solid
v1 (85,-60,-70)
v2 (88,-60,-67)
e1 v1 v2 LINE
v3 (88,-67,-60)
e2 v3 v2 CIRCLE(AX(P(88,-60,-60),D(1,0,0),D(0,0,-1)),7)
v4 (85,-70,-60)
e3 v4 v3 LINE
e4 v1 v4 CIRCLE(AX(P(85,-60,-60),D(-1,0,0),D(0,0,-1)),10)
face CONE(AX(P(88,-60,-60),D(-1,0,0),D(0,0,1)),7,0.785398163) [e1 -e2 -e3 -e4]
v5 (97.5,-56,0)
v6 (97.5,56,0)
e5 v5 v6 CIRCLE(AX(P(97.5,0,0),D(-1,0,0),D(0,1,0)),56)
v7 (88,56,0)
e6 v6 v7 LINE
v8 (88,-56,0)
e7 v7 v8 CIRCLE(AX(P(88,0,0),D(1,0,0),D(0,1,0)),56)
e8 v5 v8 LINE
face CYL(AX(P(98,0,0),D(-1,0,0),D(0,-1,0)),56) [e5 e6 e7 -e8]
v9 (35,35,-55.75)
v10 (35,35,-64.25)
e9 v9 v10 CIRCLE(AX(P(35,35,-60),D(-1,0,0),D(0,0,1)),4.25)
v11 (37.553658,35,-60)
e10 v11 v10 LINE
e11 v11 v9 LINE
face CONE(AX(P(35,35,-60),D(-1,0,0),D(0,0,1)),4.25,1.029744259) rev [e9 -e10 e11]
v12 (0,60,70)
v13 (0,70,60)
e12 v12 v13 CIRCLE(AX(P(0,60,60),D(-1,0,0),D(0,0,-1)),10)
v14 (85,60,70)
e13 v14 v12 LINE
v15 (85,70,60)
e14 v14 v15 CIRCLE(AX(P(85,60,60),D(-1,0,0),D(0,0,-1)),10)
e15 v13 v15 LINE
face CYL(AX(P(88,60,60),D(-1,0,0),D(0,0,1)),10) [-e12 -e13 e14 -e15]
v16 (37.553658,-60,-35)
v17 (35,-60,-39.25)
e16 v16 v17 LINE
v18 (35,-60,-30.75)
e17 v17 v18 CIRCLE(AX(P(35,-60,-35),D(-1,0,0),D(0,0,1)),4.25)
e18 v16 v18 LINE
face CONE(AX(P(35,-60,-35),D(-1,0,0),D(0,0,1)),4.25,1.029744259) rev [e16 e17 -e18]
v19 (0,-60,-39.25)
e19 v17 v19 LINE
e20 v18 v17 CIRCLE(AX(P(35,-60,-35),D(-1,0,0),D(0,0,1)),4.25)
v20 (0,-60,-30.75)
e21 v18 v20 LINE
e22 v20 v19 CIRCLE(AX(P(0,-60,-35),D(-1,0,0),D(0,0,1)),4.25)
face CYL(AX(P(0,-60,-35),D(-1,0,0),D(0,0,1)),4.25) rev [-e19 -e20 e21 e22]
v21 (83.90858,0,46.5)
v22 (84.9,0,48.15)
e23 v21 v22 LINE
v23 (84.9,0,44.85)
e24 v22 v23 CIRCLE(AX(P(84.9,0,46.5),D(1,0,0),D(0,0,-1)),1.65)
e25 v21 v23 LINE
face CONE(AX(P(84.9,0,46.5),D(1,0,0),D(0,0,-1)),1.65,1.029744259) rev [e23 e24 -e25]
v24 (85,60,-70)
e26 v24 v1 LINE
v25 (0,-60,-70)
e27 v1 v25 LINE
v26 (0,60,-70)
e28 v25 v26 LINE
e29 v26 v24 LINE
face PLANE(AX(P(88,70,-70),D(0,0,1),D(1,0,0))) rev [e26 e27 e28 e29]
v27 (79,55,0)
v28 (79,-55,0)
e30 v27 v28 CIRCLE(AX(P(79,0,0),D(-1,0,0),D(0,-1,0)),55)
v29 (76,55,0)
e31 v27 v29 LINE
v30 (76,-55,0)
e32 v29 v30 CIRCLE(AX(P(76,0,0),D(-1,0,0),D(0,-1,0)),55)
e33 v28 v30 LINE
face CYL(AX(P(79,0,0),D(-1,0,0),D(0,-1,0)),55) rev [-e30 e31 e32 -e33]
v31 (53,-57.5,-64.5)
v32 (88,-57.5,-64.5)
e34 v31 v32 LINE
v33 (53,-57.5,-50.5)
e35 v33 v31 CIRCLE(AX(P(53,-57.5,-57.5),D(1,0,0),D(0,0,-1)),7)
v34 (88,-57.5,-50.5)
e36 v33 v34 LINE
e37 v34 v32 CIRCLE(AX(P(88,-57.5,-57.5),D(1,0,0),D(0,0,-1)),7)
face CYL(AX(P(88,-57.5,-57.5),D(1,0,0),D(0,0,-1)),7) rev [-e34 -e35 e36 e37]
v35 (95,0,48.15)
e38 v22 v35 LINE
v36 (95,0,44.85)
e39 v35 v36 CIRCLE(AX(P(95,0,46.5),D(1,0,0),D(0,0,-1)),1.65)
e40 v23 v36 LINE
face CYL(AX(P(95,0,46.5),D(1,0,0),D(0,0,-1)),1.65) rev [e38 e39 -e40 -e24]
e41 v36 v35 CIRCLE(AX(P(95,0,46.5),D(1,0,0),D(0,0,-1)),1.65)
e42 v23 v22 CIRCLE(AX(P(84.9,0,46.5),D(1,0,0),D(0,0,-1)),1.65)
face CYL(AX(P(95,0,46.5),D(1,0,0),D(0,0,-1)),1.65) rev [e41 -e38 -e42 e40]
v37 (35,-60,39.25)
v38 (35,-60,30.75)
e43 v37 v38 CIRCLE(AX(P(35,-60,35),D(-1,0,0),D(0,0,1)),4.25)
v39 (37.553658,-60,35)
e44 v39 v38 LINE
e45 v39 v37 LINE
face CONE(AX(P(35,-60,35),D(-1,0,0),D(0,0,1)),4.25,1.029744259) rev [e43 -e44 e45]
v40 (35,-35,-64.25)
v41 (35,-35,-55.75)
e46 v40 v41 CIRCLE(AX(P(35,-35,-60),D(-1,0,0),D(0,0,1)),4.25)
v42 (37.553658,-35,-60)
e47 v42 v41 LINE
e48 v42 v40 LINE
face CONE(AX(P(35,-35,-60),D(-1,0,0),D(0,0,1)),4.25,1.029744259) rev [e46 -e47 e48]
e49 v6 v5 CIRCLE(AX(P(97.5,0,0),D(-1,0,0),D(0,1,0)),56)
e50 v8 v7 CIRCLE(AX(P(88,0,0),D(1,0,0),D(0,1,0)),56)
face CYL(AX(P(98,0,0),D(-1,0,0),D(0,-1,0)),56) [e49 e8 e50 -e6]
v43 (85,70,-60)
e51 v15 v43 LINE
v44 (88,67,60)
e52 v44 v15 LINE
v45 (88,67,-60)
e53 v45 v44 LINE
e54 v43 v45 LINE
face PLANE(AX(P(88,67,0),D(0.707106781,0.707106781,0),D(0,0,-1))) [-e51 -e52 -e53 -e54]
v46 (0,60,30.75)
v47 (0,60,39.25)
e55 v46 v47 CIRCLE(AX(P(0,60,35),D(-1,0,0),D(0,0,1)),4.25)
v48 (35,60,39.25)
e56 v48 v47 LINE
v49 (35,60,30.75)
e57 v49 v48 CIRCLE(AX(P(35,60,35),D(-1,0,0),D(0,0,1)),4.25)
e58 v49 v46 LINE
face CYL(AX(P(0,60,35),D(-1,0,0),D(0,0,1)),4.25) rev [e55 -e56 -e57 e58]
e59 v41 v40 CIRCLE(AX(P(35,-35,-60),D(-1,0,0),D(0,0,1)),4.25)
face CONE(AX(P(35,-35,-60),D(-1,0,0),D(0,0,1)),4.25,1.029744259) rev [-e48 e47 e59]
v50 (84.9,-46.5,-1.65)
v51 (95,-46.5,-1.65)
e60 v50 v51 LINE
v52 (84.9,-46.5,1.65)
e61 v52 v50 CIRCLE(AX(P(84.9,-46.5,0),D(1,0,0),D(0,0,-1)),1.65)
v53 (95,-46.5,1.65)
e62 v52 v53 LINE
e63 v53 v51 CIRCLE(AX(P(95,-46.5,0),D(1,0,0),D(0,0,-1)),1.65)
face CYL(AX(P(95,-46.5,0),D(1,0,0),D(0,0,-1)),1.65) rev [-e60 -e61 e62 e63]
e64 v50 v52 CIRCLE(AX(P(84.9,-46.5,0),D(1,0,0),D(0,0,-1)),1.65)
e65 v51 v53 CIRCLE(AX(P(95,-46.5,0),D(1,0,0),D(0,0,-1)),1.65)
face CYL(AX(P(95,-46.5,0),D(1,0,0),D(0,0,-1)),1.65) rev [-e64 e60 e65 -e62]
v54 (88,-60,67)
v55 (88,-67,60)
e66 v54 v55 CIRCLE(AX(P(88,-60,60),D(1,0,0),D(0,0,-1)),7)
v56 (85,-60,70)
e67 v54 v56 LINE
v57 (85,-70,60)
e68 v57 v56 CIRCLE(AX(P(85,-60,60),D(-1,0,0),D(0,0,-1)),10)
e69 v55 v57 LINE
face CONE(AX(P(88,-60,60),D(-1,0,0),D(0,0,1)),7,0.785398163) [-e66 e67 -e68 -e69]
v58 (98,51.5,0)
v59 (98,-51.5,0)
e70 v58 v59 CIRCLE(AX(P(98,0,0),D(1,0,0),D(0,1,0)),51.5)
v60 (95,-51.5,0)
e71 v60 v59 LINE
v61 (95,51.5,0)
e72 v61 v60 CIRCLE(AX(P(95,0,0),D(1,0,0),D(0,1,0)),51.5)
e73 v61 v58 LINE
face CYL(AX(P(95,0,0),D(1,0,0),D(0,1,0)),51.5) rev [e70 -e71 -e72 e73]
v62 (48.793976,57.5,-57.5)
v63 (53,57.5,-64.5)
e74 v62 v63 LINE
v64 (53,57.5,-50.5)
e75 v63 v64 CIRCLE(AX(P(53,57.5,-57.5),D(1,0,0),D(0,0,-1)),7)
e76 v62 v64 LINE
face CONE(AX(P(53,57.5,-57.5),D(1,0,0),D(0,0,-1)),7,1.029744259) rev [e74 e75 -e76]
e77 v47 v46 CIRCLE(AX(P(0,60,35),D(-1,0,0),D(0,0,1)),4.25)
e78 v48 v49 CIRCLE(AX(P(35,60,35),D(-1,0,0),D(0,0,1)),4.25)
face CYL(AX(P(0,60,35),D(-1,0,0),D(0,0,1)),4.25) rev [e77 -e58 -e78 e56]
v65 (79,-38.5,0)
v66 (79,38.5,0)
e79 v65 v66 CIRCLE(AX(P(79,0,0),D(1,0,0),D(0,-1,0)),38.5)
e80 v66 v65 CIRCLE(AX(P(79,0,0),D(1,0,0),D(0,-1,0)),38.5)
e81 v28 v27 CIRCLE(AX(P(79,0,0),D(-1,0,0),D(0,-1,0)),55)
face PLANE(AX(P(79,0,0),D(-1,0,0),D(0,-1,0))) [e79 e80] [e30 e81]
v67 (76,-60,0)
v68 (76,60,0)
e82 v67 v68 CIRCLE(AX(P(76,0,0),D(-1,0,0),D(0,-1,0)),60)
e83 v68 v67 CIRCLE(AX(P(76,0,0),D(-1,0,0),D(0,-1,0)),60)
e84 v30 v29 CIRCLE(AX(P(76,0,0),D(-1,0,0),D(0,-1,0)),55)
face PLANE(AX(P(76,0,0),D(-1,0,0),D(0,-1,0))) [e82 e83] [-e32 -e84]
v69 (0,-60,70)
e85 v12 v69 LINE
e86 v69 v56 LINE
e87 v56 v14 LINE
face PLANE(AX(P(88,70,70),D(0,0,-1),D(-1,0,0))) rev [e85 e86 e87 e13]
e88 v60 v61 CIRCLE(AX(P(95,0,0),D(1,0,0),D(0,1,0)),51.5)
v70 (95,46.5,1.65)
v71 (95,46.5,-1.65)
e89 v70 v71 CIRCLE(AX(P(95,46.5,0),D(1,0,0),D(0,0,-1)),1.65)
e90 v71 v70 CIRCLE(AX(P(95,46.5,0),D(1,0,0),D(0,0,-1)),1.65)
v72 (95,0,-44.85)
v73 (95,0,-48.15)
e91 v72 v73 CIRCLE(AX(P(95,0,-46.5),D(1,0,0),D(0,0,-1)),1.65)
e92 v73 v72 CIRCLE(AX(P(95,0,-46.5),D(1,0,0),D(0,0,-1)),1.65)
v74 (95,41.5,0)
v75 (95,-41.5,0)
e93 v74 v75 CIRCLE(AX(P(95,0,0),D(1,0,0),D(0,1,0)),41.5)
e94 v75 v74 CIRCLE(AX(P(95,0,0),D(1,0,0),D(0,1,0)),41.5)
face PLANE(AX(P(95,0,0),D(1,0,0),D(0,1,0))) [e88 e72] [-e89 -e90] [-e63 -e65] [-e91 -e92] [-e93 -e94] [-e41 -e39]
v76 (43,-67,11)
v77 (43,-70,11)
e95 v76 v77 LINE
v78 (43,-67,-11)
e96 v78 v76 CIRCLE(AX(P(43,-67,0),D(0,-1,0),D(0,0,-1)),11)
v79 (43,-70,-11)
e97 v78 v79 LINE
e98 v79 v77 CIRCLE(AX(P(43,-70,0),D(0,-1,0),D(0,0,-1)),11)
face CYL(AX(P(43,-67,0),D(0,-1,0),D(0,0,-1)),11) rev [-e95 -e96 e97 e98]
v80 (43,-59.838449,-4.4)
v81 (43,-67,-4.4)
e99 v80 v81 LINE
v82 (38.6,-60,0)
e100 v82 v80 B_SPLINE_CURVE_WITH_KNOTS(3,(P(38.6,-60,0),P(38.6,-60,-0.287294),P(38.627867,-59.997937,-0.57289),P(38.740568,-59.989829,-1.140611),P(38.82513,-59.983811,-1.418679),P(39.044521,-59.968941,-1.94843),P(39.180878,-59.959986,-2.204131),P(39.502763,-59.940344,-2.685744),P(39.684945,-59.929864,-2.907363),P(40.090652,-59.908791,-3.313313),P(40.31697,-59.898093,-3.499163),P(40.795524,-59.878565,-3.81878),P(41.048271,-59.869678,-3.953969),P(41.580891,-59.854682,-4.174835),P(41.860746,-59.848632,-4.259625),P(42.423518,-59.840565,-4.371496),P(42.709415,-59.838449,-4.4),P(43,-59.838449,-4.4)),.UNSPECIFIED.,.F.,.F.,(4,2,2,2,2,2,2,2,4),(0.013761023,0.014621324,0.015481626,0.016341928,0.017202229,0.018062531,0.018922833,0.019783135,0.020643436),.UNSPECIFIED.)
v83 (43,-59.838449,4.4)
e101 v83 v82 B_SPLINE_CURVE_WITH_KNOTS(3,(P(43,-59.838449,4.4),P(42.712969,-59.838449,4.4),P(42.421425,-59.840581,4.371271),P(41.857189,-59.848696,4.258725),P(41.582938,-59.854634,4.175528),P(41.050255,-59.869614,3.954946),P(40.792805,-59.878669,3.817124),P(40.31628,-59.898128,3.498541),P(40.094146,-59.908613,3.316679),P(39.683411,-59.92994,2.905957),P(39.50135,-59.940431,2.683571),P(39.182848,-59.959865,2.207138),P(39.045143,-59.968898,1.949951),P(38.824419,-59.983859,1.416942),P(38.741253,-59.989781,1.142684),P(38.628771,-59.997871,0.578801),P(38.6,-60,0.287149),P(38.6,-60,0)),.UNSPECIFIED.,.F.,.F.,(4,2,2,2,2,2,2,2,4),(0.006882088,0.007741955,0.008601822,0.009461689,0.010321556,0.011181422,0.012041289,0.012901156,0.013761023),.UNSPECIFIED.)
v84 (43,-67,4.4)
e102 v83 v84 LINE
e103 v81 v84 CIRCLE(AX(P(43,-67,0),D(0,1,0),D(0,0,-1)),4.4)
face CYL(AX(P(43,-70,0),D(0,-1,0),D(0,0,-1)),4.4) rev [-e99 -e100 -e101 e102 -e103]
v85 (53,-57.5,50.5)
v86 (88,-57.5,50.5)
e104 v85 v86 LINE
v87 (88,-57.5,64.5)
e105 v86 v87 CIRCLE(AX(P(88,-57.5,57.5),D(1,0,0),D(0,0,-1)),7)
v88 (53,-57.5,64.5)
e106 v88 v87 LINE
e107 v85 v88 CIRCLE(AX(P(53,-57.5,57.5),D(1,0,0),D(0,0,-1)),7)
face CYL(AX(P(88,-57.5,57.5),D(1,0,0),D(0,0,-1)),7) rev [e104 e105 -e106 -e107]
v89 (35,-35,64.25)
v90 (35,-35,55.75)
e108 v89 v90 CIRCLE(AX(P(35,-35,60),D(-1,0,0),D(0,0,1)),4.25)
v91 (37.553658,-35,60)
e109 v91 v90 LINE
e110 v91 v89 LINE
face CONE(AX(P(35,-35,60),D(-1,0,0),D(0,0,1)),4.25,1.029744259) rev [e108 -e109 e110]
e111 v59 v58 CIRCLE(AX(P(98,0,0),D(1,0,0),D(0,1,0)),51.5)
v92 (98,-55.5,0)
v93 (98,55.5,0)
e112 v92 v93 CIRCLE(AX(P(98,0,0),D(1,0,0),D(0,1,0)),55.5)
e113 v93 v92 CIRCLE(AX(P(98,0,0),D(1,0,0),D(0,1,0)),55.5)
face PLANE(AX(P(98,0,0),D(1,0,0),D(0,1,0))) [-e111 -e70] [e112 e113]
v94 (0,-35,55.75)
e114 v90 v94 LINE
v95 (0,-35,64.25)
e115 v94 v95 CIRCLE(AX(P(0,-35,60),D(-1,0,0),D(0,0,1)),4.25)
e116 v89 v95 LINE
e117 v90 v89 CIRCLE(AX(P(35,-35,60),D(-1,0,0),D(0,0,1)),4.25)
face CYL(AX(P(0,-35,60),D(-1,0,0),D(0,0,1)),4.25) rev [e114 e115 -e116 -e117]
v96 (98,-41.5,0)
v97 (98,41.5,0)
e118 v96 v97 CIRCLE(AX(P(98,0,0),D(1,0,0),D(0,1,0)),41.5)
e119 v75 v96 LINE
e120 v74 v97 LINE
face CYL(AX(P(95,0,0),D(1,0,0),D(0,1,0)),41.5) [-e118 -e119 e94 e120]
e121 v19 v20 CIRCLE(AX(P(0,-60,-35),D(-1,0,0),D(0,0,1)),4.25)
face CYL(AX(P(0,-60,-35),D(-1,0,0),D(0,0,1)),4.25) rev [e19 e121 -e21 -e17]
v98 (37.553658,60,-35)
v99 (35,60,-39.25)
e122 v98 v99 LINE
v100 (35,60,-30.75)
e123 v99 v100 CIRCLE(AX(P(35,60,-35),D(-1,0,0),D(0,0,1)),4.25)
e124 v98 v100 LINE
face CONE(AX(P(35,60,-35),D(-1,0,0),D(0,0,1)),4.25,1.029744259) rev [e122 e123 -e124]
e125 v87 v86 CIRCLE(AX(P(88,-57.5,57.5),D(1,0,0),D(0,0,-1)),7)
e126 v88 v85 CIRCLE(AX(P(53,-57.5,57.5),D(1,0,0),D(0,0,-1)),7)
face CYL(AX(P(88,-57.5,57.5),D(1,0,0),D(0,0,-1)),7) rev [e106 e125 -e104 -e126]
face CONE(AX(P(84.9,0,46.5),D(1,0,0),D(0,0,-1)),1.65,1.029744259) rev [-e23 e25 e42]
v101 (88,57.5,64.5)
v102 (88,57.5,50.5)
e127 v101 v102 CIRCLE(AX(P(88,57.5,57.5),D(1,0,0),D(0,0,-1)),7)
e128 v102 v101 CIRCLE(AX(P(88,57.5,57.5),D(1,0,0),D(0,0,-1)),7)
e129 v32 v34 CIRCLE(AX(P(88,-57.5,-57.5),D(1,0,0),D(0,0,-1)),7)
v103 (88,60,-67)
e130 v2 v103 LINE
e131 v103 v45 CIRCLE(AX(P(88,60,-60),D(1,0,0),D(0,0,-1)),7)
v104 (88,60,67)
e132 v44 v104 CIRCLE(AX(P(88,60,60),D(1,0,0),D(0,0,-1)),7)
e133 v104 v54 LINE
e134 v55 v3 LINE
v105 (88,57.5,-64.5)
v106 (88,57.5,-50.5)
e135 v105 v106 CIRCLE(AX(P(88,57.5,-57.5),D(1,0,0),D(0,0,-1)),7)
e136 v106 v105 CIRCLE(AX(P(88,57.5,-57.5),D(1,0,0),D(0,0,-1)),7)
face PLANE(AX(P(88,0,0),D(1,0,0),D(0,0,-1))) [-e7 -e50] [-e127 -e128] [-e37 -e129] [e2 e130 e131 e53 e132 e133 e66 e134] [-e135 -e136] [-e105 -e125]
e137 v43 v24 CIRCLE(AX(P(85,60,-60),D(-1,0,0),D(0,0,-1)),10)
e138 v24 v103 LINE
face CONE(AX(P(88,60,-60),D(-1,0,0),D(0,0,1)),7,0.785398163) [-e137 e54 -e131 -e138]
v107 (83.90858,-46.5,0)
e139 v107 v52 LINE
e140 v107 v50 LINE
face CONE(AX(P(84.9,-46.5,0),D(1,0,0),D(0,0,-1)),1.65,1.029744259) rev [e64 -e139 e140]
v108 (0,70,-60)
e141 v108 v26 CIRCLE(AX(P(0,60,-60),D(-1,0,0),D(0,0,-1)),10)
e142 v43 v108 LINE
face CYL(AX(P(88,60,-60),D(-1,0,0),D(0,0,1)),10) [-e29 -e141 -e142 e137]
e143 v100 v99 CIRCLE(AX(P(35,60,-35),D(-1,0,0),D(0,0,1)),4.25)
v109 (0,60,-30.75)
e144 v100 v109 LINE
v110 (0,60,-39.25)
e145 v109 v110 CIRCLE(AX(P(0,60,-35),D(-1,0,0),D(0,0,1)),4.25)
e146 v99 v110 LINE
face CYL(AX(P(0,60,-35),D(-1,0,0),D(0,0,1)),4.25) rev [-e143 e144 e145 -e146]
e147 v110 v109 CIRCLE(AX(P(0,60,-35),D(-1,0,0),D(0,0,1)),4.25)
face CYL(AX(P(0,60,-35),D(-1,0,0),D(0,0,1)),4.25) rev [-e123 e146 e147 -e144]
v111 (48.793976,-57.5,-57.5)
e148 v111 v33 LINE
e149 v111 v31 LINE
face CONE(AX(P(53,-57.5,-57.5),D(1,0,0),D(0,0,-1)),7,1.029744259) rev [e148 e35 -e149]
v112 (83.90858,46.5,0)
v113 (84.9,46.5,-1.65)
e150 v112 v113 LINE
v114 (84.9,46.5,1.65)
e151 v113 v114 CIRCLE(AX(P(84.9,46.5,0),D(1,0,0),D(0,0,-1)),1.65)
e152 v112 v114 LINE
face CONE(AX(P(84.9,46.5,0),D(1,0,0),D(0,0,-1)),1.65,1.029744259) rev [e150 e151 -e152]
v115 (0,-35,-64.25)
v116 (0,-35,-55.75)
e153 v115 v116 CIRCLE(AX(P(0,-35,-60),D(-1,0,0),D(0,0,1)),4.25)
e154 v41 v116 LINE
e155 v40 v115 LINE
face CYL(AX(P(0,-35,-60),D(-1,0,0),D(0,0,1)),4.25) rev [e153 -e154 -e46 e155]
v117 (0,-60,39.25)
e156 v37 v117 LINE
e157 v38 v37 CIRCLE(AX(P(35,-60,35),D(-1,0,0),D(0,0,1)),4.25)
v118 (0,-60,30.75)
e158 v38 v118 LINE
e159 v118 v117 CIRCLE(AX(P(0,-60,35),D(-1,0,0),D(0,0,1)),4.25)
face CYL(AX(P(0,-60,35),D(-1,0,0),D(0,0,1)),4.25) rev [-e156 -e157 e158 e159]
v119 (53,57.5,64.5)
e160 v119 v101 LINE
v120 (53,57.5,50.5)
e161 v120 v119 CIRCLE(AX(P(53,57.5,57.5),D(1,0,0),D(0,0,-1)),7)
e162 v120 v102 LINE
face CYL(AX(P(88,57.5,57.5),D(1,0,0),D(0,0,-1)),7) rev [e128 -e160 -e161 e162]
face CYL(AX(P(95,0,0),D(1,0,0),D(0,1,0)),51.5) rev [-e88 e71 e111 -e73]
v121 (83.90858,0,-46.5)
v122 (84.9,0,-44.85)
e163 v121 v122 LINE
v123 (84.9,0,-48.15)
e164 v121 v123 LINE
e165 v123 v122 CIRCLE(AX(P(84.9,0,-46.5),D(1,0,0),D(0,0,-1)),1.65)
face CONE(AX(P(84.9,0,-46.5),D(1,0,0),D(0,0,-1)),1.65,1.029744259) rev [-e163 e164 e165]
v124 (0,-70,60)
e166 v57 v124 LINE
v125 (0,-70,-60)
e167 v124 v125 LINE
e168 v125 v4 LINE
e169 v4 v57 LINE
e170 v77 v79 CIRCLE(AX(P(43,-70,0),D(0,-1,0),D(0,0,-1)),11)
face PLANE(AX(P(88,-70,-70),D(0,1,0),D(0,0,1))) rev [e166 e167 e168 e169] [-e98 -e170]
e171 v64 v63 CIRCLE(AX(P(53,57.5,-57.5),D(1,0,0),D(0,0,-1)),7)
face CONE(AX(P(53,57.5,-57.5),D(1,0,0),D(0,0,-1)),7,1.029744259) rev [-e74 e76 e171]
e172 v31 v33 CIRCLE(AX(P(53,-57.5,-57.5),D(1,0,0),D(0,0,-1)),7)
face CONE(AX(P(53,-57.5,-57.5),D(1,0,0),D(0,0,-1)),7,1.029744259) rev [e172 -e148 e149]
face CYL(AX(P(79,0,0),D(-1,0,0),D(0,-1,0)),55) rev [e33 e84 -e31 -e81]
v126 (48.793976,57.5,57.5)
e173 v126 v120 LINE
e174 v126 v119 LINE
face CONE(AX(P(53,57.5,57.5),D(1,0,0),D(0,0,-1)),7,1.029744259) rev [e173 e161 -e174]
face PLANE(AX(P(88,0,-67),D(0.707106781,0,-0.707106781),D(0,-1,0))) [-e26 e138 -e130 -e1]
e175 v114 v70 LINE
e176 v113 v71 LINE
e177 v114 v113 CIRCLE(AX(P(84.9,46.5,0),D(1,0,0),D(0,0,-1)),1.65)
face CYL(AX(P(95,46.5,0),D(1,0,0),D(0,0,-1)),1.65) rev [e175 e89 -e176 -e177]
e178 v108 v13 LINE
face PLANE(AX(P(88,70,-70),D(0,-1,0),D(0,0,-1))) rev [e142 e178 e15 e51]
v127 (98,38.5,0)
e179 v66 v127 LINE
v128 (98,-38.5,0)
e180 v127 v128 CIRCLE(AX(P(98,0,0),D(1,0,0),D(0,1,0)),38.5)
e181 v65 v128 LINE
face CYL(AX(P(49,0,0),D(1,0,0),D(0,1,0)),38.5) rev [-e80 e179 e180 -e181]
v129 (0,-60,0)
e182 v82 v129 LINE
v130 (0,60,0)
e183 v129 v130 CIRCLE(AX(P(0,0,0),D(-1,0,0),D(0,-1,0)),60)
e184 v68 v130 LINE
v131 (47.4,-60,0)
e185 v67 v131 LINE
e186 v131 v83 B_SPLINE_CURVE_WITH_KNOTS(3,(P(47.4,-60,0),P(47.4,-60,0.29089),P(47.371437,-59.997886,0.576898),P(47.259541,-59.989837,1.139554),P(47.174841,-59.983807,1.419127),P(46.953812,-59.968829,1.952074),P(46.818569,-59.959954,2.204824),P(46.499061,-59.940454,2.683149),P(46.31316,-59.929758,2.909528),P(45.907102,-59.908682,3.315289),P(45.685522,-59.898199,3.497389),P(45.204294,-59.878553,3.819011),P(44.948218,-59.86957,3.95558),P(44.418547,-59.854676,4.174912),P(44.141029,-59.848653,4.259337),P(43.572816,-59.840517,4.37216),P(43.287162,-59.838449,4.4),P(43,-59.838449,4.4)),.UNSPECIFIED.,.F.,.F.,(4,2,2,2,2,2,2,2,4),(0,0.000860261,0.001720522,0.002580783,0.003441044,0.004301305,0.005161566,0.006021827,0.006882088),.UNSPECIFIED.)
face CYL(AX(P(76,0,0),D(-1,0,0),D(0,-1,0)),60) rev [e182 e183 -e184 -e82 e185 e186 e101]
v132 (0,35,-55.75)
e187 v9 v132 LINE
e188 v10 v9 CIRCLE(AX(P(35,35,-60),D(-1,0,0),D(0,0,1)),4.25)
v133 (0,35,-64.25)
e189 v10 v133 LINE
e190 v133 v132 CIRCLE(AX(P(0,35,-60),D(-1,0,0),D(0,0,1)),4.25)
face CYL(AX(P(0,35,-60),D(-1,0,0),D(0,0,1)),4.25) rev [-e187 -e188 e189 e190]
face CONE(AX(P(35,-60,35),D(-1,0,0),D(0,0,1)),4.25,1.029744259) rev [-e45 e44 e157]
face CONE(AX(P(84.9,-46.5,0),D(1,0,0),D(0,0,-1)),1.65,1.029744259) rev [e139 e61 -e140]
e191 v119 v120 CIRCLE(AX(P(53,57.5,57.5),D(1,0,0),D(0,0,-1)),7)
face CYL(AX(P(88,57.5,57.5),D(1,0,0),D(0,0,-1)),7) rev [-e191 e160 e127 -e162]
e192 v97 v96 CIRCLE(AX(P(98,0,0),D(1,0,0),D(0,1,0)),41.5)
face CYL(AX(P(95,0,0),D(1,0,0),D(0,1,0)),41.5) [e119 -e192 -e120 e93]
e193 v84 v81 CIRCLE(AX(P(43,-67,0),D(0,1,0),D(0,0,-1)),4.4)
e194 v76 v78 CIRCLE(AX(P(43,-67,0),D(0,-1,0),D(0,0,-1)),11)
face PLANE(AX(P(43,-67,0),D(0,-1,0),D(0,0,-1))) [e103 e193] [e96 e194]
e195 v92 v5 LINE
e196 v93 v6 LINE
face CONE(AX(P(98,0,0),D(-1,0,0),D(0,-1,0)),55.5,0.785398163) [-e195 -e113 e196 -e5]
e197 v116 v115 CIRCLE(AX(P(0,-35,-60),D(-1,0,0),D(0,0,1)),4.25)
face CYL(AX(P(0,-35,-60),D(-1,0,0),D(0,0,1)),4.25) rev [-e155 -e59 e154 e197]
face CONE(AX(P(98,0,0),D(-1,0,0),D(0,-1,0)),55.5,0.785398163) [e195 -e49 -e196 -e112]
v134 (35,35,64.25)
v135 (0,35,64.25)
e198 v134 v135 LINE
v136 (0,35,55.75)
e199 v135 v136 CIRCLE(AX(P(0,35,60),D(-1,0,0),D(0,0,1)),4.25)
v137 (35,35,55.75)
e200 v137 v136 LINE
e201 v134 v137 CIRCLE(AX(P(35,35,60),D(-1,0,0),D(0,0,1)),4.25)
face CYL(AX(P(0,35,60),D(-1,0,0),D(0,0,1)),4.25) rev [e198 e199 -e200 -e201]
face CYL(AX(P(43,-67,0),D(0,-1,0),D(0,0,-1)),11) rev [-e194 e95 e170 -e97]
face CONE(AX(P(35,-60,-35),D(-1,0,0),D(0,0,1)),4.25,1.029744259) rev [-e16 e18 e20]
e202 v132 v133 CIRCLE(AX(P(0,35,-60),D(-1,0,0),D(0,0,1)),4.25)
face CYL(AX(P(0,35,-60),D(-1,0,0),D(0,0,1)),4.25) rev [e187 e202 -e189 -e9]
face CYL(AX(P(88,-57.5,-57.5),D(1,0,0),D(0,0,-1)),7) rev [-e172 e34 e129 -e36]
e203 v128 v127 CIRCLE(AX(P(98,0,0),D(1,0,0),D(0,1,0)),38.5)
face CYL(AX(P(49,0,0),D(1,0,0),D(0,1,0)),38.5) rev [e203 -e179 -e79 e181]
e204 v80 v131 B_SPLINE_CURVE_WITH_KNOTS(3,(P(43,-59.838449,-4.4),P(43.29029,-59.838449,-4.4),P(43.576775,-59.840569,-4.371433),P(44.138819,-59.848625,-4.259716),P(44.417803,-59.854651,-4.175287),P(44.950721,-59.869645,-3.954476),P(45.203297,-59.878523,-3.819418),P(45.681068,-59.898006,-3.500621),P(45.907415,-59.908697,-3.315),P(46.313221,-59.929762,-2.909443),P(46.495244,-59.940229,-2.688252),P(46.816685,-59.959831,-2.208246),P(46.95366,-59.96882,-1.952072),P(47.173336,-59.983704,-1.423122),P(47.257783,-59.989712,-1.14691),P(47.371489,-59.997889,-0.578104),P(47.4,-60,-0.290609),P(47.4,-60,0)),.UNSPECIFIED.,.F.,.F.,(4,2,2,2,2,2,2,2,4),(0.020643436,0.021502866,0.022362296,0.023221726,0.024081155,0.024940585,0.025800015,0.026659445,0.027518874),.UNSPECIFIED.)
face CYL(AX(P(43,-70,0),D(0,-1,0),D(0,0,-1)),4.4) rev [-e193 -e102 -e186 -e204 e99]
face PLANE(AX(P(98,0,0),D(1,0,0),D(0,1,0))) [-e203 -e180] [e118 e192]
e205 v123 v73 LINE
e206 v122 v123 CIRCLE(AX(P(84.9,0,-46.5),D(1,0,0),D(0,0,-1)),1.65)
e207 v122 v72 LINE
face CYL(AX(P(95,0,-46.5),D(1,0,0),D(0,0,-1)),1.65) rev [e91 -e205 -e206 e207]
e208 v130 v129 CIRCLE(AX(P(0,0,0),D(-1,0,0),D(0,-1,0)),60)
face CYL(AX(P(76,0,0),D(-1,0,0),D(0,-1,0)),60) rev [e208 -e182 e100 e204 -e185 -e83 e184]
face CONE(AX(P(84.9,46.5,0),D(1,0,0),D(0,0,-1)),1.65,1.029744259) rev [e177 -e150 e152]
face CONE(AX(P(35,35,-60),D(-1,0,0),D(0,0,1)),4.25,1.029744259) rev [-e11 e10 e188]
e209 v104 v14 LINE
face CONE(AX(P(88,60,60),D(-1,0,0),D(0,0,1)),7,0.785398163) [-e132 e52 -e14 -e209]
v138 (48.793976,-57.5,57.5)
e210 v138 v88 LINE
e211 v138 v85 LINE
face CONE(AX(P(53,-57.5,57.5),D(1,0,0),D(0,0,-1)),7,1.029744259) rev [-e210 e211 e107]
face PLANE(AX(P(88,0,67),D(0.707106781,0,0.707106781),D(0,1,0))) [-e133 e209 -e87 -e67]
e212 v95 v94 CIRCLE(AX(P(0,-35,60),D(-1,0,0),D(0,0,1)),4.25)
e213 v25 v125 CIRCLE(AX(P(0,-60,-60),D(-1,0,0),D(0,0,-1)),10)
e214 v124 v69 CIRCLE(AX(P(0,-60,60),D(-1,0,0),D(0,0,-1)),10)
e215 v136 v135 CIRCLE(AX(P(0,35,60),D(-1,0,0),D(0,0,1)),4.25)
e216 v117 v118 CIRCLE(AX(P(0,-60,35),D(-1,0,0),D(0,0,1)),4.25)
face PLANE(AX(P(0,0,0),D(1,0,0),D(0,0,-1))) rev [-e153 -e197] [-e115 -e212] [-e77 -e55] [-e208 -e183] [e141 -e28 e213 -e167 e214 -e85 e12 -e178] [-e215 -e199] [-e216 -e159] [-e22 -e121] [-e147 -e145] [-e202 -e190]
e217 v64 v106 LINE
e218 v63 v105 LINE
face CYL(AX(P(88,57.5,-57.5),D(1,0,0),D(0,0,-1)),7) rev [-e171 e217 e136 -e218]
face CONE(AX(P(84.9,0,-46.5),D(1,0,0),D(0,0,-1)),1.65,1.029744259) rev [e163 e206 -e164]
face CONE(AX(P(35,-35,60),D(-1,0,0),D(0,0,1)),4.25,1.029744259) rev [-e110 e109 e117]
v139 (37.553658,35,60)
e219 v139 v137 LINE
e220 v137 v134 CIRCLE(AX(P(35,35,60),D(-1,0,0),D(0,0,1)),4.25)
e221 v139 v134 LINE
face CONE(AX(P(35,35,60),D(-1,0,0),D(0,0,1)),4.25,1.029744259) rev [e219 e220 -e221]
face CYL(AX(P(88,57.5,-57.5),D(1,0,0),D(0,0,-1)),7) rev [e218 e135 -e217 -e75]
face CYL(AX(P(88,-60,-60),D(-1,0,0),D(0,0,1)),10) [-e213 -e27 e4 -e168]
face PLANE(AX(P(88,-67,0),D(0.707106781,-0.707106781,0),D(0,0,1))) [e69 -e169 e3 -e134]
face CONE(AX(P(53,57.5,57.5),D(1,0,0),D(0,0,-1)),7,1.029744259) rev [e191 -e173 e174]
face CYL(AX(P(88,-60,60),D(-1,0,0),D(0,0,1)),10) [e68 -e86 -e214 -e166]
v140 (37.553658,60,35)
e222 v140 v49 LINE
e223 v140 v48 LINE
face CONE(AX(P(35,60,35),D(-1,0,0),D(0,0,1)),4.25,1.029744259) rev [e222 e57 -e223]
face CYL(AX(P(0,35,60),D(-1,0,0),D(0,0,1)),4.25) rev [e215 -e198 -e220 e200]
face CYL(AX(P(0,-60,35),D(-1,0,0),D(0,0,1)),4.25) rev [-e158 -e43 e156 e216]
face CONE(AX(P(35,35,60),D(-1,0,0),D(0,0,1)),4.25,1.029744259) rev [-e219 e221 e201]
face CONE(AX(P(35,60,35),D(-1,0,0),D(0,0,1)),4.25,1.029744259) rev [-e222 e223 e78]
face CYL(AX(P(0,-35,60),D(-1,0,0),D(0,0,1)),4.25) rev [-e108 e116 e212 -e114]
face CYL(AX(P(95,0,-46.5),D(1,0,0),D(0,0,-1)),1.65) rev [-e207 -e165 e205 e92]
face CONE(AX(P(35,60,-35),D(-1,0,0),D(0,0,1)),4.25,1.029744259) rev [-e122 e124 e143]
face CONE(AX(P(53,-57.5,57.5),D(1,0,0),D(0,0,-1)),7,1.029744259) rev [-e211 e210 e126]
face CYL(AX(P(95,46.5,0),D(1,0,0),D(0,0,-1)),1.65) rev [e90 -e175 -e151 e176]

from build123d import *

# Parameters (mm, degrees)
SKETCH1_W               = 140
SKETCH1_H               = 140
BOSS_EXTRUDE1_DEPTH     = 88
SKETCH2_R               = 56
BOSS_EXTRUDE2_DEPTH     = 10
SKETCH3_R               = 60
CUT_EXTRUDE1_DEPTH      = 76
SKETCH4_R               = 38.5
CUT_EXTRUDE2_DEPTH      = 49
M10_TAPPED_HOLE1_D      = 8.5
M10_TAPPED_HOLE1_DEPTH  = 35
M10_TAPPED_HOLE1_TIP    = 2.553657631
M16_TAPPED_HOLE1_D      = 14
M16_TAPPED_HOLE1_DEPTH  = 35
M16_TAPPED_HOLE1_TIP    = 4.206024333
SKETCH14_R              = 55
CUT_EXTRUDE5_DEPTH      = 3
CHAMFER2_SIZE           = 0.5
BOSS_EXTRUDE3_START     = 44
SKETCH17_R              = 60
BOSS_EXTRUDE3_DEPTH     = 15
SKETCH18_R              = 55
CUT_EXTRUDE7_DEPTH      = 15
SKETCH22_R              = 60
CUT_EXTRUDE8_DEPTH      = 15
SKETCH23_R              = 51.5
SKETCH23_R_2            = 41.5
CUT_EXTRUDE9_DEPTH      = 3
CIRPATTERN1_COUNT       = 4
FILLET1_R               = 10
CHAMFER6_SIZE           = 3
SKETCH30_R              = 2.5
CUT_EXTRUDE12_DEPTH     = 12
G1_8_TAPPED_HOLE1_D     = 8.8
G1_8_TAPPED_HOLE1_DEPTH = 22.18
G1_8_TAPPED_HOLE1_TIP   = 2.643786724
SKETCH34_R              = 11
CUT_EXTRUDE14_DEPTH     = 3


with BuildPart() as part:
    # Sketch1 → Boss-Extrude1 (new body)
    with BuildSketch(Plane(origin=(0, 0, 0), x_dir=(0, -1, 0), z_dir=(1, 0, 0))):
        Rectangle(SKETCH1_W, SKETCH1_H)
    extrude(amount=BOSS_EXTRUDE1_DEPTH)

    # Sketch2 → Boss-Extrude2 (add)
    with BuildSketch(Plane(origin=(88, 0, 0), x_dir=(0, -1, 0), z_dir=(1, 0, 0))):
        with Locations(Location((0, 0, 0), (0, 0, 180))):
            Circle(SKETCH2_R)
    extrude(amount=BOSS_EXTRUDE2_DEPTH)

    # Sketch3 → Cut-Extrude1 (cut)
    with BuildSketch(Plane(origin=(0, 0, 0), x_dir=(0, -1, 0), z_dir=(-1, 0, 0))):
        Circle(SKETCH3_R)
    extrude(amount=-CUT_EXTRUDE1_DEPTH, mode=Mode.SUBTRACT)

    # Sketch4 → Cut-Extrude2 (cut)
    with BuildSketch(Plane(origin=(98, 0, 0), x_dir=(0, -1, 0), z_dir=(1, 0, 0))):
        with Locations(Location((0, 0, 0), (0, 0, 180))):
            Circle(SKETCH4_R)
    extrude(amount=-CUT_EXTRUDE2_DEPTH, mode=Mode.SUBTRACT)

    # M10 Tapped Hole1
    with Locations(Plane(origin=(0, 0, 0), x_dir=(0, 1, 0), z_dir=(-1, 0, 0))):
        with Locations((-35, 60), (35, 60), (60, 35), (60, -35), (35, -60), (-35, -60), (-60, -35), (-60, 35)):
            Hole(M10_TAPPED_HOLE1_D / 2, depth=M10_TAPPED_HOLE1_DEPTH)
            with Locations((0, 0, -(M10_TAPPED_HOLE1_DEPTH + M10_TAPPED_HOLE1_TIP / 2))):  # 118° drill point
                Cone(0, M10_TAPPED_HOLE1_D / 2, M10_TAPPED_HOLE1_TIP, mode=Mode.SUBTRACT)

    # M16 Tapped Hole1
    with Locations(Plane(origin=(88, 0, 0), x_dir=(0, -1, 0), z_dir=(1, 0, 0))):
        with Locations((57.5, 57.5), (-57.5, 57.5), (-57.5, -57.5), (57.5, -57.5)):
            Hole(M16_TAPPED_HOLE1_D / 2, depth=M16_TAPPED_HOLE1_DEPTH)
            with Locations((0, 0, -(M16_TAPPED_HOLE1_DEPTH + M16_TAPPED_HOLE1_TIP / 2))):  # 118° drill point
                Cone(0, M16_TAPPED_HOLE1_D / 2, M16_TAPPED_HOLE1_TIP, mode=Mode.SUBTRACT)

    # Sketch14 → Cut-Extrude5 (cut)
    with BuildSketch(Plane(origin=(76, 0, 0), x_dir=(0, -1, 0), z_dir=(-1, 0, 0))):
        Circle(SKETCH14_R)
    extrude(amount=-CUT_EXTRUDE5_DEPTH, mode=Mode.SUBTRACT)

    # Chamfer2
    chamfer2_edges = [part.edges().sort_by_distance(p)[0] for p in [
        (98, -56, 0),
    ]]
    chamfer(chamfer2_edges, length=CHAMFER2_SIZE)

    # Sketch17 → Boss-Extrude3 (add)
    with BuildSketch(Plane.ZY.offset(-76).offset(BOSS_EXTRUDE3_START)):
        with Locations(Location((0, 0, 0), (0, 0, 270))):
            Circle(SKETCH17_R)
    extrude(amount=-BOSS_EXTRUDE3_DEPTH)

    # Sketch18 → Cut-Extrude7 (cut)
    with BuildSketch(Plane.ZY.offset(-32)):
        with Locations(Location((0, 0, 0), (0, 0, 270))):
            Circle(SKETCH18_R)
    extrude(amount=-CUT_EXTRUDE7_DEPTH, mode=Mode.SUBTRACT)

    # Sketch22 → Cut-Extrude8 (cut)
    with BuildSketch(Plane.ZY.offset(-32)):
        with Locations(Location((0, 0, 0), (0, 0, 270))):
            Circle(SKETCH22_R)
    extrude(amount=-CUT_EXTRUDE8_DEPTH, mode=Mode.SUBTRACT)

    # Sketch23 → Cut-Extrude9 (cut)
    with BuildSketch(Plane(origin=(98, 0, 0), x_dir=(0, 0, -1), z_dir=(1, 0, 0))):
        with Locations(Location((0, 0, 0), (0, 0, 90))):
            Circle(SKETCH23_R)
        with Locations(Location((0, 0, 0), (0, 0, 90))):
            Circle(SKETCH23_R_2, mode=Mode.SUBTRACT)
    extrude(amount=-CUT_EXTRUDE9_DEPTH, mode=Mode.SUBTRACT)

    # Sketch25 → M4 Tapped Hole2 (revolve, cut)
    with BuildSketch(Plane(origin=(95, 46.5, 0), x_dir=(0, 0, -1), z_dir=(0, 1, 0))):
        Polygon((0, 0), (0, 11.091420021), (1.65, 10.1), (1.65, 0), align=None)
    m4_tapped_hole2 = revolve(axis=Axis((101.35, 46.5, 0), (-1, 0, 0)), mode=Mode.SUBTRACT)

    # CirPattern1: M4 Tapped Hole2 ×4 about axis
    cirpattern1_axis = Axis((0, 0, 0), (1, 0, 0))
    for i in range(1, CIRPATTERN1_COUNT):
        add(m4_tapped_hole2.rotate(cirpattern1_axis, i * 360 / CIRPATTERN1_COUNT), mode=Mode.SUBTRACT)

    # Fillet1
    fillet1_edges = [part.edges().sort_by_distance(p)[0] for p in [
        (44, -70, 70),
        (44, 70, 70),
        (44, 70, -70),
        (44, -70, -70),
    ]]
    fillet(fillet1_edges, radius=FILLET1_R)

    # Chamfer6
    chamfer6_edges = [part.edges().sort_by_distance(p)[0] for p in [
        (88, 0, -70),
        (88, -70, 0),
        (88, 70, 0),
        (88, 0, 70),
        (88, 67.071067812, 67.071067812),
        (88, 67.071067812, -67.071067812),
        (88, -67.071067812, 67.071067812),
        (88, -67.071067812, -67.071067812),
    ]]
    chamfer(chamfer6_edges, length=CHAMFER6_SIZE)

    # Sketch30 → Cut-Extrude12 (cut)
    with BuildSketch(Plane.XZ.offset(70)):
        with Locations(Location((43, 0, 0), (0, 0, 270))):
            Circle(SKETCH30_R)
    extrude(amount=-CUT_EXTRUDE12_DEPTH, mode=Mode.SUBTRACT)

    # G1/8 Tapped Hole1
    with Locations(Plane(origin=(0, -70, 0), x_dir=(-1, 0, 0), z_dir=(0, -1, 0))):
        with Locations((-43, 0)):
            Hole(G1_8_TAPPED_HOLE1_D / 2, depth=G1_8_TAPPED_HOLE1_DEPTH)
            with Locations((0, 0, -(G1_8_TAPPED_HOLE1_DEPTH + G1_8_TAPPED_HOLE1_TIP / 2))):  # 118° drill point
                Cone(0, G1_8_TAPPED_HOLE1_D / 2, G1_8_TAPPED_HOLE1_TIP, mode=Mode.SUBTRACT)

    # Sketch34 → Cut-Extrude14 (cut)
    with BuildSketch(Plane.XZ.offset(70)):
        with Locations(Location((43, 0, 0), (0, 0, 270))):
            Circle(SKETCH34_R)
    extrude(amount=-CUT_EXTRUDE14_DEPTH, mode=Mode.SUBTRACT)


solid = part.part
